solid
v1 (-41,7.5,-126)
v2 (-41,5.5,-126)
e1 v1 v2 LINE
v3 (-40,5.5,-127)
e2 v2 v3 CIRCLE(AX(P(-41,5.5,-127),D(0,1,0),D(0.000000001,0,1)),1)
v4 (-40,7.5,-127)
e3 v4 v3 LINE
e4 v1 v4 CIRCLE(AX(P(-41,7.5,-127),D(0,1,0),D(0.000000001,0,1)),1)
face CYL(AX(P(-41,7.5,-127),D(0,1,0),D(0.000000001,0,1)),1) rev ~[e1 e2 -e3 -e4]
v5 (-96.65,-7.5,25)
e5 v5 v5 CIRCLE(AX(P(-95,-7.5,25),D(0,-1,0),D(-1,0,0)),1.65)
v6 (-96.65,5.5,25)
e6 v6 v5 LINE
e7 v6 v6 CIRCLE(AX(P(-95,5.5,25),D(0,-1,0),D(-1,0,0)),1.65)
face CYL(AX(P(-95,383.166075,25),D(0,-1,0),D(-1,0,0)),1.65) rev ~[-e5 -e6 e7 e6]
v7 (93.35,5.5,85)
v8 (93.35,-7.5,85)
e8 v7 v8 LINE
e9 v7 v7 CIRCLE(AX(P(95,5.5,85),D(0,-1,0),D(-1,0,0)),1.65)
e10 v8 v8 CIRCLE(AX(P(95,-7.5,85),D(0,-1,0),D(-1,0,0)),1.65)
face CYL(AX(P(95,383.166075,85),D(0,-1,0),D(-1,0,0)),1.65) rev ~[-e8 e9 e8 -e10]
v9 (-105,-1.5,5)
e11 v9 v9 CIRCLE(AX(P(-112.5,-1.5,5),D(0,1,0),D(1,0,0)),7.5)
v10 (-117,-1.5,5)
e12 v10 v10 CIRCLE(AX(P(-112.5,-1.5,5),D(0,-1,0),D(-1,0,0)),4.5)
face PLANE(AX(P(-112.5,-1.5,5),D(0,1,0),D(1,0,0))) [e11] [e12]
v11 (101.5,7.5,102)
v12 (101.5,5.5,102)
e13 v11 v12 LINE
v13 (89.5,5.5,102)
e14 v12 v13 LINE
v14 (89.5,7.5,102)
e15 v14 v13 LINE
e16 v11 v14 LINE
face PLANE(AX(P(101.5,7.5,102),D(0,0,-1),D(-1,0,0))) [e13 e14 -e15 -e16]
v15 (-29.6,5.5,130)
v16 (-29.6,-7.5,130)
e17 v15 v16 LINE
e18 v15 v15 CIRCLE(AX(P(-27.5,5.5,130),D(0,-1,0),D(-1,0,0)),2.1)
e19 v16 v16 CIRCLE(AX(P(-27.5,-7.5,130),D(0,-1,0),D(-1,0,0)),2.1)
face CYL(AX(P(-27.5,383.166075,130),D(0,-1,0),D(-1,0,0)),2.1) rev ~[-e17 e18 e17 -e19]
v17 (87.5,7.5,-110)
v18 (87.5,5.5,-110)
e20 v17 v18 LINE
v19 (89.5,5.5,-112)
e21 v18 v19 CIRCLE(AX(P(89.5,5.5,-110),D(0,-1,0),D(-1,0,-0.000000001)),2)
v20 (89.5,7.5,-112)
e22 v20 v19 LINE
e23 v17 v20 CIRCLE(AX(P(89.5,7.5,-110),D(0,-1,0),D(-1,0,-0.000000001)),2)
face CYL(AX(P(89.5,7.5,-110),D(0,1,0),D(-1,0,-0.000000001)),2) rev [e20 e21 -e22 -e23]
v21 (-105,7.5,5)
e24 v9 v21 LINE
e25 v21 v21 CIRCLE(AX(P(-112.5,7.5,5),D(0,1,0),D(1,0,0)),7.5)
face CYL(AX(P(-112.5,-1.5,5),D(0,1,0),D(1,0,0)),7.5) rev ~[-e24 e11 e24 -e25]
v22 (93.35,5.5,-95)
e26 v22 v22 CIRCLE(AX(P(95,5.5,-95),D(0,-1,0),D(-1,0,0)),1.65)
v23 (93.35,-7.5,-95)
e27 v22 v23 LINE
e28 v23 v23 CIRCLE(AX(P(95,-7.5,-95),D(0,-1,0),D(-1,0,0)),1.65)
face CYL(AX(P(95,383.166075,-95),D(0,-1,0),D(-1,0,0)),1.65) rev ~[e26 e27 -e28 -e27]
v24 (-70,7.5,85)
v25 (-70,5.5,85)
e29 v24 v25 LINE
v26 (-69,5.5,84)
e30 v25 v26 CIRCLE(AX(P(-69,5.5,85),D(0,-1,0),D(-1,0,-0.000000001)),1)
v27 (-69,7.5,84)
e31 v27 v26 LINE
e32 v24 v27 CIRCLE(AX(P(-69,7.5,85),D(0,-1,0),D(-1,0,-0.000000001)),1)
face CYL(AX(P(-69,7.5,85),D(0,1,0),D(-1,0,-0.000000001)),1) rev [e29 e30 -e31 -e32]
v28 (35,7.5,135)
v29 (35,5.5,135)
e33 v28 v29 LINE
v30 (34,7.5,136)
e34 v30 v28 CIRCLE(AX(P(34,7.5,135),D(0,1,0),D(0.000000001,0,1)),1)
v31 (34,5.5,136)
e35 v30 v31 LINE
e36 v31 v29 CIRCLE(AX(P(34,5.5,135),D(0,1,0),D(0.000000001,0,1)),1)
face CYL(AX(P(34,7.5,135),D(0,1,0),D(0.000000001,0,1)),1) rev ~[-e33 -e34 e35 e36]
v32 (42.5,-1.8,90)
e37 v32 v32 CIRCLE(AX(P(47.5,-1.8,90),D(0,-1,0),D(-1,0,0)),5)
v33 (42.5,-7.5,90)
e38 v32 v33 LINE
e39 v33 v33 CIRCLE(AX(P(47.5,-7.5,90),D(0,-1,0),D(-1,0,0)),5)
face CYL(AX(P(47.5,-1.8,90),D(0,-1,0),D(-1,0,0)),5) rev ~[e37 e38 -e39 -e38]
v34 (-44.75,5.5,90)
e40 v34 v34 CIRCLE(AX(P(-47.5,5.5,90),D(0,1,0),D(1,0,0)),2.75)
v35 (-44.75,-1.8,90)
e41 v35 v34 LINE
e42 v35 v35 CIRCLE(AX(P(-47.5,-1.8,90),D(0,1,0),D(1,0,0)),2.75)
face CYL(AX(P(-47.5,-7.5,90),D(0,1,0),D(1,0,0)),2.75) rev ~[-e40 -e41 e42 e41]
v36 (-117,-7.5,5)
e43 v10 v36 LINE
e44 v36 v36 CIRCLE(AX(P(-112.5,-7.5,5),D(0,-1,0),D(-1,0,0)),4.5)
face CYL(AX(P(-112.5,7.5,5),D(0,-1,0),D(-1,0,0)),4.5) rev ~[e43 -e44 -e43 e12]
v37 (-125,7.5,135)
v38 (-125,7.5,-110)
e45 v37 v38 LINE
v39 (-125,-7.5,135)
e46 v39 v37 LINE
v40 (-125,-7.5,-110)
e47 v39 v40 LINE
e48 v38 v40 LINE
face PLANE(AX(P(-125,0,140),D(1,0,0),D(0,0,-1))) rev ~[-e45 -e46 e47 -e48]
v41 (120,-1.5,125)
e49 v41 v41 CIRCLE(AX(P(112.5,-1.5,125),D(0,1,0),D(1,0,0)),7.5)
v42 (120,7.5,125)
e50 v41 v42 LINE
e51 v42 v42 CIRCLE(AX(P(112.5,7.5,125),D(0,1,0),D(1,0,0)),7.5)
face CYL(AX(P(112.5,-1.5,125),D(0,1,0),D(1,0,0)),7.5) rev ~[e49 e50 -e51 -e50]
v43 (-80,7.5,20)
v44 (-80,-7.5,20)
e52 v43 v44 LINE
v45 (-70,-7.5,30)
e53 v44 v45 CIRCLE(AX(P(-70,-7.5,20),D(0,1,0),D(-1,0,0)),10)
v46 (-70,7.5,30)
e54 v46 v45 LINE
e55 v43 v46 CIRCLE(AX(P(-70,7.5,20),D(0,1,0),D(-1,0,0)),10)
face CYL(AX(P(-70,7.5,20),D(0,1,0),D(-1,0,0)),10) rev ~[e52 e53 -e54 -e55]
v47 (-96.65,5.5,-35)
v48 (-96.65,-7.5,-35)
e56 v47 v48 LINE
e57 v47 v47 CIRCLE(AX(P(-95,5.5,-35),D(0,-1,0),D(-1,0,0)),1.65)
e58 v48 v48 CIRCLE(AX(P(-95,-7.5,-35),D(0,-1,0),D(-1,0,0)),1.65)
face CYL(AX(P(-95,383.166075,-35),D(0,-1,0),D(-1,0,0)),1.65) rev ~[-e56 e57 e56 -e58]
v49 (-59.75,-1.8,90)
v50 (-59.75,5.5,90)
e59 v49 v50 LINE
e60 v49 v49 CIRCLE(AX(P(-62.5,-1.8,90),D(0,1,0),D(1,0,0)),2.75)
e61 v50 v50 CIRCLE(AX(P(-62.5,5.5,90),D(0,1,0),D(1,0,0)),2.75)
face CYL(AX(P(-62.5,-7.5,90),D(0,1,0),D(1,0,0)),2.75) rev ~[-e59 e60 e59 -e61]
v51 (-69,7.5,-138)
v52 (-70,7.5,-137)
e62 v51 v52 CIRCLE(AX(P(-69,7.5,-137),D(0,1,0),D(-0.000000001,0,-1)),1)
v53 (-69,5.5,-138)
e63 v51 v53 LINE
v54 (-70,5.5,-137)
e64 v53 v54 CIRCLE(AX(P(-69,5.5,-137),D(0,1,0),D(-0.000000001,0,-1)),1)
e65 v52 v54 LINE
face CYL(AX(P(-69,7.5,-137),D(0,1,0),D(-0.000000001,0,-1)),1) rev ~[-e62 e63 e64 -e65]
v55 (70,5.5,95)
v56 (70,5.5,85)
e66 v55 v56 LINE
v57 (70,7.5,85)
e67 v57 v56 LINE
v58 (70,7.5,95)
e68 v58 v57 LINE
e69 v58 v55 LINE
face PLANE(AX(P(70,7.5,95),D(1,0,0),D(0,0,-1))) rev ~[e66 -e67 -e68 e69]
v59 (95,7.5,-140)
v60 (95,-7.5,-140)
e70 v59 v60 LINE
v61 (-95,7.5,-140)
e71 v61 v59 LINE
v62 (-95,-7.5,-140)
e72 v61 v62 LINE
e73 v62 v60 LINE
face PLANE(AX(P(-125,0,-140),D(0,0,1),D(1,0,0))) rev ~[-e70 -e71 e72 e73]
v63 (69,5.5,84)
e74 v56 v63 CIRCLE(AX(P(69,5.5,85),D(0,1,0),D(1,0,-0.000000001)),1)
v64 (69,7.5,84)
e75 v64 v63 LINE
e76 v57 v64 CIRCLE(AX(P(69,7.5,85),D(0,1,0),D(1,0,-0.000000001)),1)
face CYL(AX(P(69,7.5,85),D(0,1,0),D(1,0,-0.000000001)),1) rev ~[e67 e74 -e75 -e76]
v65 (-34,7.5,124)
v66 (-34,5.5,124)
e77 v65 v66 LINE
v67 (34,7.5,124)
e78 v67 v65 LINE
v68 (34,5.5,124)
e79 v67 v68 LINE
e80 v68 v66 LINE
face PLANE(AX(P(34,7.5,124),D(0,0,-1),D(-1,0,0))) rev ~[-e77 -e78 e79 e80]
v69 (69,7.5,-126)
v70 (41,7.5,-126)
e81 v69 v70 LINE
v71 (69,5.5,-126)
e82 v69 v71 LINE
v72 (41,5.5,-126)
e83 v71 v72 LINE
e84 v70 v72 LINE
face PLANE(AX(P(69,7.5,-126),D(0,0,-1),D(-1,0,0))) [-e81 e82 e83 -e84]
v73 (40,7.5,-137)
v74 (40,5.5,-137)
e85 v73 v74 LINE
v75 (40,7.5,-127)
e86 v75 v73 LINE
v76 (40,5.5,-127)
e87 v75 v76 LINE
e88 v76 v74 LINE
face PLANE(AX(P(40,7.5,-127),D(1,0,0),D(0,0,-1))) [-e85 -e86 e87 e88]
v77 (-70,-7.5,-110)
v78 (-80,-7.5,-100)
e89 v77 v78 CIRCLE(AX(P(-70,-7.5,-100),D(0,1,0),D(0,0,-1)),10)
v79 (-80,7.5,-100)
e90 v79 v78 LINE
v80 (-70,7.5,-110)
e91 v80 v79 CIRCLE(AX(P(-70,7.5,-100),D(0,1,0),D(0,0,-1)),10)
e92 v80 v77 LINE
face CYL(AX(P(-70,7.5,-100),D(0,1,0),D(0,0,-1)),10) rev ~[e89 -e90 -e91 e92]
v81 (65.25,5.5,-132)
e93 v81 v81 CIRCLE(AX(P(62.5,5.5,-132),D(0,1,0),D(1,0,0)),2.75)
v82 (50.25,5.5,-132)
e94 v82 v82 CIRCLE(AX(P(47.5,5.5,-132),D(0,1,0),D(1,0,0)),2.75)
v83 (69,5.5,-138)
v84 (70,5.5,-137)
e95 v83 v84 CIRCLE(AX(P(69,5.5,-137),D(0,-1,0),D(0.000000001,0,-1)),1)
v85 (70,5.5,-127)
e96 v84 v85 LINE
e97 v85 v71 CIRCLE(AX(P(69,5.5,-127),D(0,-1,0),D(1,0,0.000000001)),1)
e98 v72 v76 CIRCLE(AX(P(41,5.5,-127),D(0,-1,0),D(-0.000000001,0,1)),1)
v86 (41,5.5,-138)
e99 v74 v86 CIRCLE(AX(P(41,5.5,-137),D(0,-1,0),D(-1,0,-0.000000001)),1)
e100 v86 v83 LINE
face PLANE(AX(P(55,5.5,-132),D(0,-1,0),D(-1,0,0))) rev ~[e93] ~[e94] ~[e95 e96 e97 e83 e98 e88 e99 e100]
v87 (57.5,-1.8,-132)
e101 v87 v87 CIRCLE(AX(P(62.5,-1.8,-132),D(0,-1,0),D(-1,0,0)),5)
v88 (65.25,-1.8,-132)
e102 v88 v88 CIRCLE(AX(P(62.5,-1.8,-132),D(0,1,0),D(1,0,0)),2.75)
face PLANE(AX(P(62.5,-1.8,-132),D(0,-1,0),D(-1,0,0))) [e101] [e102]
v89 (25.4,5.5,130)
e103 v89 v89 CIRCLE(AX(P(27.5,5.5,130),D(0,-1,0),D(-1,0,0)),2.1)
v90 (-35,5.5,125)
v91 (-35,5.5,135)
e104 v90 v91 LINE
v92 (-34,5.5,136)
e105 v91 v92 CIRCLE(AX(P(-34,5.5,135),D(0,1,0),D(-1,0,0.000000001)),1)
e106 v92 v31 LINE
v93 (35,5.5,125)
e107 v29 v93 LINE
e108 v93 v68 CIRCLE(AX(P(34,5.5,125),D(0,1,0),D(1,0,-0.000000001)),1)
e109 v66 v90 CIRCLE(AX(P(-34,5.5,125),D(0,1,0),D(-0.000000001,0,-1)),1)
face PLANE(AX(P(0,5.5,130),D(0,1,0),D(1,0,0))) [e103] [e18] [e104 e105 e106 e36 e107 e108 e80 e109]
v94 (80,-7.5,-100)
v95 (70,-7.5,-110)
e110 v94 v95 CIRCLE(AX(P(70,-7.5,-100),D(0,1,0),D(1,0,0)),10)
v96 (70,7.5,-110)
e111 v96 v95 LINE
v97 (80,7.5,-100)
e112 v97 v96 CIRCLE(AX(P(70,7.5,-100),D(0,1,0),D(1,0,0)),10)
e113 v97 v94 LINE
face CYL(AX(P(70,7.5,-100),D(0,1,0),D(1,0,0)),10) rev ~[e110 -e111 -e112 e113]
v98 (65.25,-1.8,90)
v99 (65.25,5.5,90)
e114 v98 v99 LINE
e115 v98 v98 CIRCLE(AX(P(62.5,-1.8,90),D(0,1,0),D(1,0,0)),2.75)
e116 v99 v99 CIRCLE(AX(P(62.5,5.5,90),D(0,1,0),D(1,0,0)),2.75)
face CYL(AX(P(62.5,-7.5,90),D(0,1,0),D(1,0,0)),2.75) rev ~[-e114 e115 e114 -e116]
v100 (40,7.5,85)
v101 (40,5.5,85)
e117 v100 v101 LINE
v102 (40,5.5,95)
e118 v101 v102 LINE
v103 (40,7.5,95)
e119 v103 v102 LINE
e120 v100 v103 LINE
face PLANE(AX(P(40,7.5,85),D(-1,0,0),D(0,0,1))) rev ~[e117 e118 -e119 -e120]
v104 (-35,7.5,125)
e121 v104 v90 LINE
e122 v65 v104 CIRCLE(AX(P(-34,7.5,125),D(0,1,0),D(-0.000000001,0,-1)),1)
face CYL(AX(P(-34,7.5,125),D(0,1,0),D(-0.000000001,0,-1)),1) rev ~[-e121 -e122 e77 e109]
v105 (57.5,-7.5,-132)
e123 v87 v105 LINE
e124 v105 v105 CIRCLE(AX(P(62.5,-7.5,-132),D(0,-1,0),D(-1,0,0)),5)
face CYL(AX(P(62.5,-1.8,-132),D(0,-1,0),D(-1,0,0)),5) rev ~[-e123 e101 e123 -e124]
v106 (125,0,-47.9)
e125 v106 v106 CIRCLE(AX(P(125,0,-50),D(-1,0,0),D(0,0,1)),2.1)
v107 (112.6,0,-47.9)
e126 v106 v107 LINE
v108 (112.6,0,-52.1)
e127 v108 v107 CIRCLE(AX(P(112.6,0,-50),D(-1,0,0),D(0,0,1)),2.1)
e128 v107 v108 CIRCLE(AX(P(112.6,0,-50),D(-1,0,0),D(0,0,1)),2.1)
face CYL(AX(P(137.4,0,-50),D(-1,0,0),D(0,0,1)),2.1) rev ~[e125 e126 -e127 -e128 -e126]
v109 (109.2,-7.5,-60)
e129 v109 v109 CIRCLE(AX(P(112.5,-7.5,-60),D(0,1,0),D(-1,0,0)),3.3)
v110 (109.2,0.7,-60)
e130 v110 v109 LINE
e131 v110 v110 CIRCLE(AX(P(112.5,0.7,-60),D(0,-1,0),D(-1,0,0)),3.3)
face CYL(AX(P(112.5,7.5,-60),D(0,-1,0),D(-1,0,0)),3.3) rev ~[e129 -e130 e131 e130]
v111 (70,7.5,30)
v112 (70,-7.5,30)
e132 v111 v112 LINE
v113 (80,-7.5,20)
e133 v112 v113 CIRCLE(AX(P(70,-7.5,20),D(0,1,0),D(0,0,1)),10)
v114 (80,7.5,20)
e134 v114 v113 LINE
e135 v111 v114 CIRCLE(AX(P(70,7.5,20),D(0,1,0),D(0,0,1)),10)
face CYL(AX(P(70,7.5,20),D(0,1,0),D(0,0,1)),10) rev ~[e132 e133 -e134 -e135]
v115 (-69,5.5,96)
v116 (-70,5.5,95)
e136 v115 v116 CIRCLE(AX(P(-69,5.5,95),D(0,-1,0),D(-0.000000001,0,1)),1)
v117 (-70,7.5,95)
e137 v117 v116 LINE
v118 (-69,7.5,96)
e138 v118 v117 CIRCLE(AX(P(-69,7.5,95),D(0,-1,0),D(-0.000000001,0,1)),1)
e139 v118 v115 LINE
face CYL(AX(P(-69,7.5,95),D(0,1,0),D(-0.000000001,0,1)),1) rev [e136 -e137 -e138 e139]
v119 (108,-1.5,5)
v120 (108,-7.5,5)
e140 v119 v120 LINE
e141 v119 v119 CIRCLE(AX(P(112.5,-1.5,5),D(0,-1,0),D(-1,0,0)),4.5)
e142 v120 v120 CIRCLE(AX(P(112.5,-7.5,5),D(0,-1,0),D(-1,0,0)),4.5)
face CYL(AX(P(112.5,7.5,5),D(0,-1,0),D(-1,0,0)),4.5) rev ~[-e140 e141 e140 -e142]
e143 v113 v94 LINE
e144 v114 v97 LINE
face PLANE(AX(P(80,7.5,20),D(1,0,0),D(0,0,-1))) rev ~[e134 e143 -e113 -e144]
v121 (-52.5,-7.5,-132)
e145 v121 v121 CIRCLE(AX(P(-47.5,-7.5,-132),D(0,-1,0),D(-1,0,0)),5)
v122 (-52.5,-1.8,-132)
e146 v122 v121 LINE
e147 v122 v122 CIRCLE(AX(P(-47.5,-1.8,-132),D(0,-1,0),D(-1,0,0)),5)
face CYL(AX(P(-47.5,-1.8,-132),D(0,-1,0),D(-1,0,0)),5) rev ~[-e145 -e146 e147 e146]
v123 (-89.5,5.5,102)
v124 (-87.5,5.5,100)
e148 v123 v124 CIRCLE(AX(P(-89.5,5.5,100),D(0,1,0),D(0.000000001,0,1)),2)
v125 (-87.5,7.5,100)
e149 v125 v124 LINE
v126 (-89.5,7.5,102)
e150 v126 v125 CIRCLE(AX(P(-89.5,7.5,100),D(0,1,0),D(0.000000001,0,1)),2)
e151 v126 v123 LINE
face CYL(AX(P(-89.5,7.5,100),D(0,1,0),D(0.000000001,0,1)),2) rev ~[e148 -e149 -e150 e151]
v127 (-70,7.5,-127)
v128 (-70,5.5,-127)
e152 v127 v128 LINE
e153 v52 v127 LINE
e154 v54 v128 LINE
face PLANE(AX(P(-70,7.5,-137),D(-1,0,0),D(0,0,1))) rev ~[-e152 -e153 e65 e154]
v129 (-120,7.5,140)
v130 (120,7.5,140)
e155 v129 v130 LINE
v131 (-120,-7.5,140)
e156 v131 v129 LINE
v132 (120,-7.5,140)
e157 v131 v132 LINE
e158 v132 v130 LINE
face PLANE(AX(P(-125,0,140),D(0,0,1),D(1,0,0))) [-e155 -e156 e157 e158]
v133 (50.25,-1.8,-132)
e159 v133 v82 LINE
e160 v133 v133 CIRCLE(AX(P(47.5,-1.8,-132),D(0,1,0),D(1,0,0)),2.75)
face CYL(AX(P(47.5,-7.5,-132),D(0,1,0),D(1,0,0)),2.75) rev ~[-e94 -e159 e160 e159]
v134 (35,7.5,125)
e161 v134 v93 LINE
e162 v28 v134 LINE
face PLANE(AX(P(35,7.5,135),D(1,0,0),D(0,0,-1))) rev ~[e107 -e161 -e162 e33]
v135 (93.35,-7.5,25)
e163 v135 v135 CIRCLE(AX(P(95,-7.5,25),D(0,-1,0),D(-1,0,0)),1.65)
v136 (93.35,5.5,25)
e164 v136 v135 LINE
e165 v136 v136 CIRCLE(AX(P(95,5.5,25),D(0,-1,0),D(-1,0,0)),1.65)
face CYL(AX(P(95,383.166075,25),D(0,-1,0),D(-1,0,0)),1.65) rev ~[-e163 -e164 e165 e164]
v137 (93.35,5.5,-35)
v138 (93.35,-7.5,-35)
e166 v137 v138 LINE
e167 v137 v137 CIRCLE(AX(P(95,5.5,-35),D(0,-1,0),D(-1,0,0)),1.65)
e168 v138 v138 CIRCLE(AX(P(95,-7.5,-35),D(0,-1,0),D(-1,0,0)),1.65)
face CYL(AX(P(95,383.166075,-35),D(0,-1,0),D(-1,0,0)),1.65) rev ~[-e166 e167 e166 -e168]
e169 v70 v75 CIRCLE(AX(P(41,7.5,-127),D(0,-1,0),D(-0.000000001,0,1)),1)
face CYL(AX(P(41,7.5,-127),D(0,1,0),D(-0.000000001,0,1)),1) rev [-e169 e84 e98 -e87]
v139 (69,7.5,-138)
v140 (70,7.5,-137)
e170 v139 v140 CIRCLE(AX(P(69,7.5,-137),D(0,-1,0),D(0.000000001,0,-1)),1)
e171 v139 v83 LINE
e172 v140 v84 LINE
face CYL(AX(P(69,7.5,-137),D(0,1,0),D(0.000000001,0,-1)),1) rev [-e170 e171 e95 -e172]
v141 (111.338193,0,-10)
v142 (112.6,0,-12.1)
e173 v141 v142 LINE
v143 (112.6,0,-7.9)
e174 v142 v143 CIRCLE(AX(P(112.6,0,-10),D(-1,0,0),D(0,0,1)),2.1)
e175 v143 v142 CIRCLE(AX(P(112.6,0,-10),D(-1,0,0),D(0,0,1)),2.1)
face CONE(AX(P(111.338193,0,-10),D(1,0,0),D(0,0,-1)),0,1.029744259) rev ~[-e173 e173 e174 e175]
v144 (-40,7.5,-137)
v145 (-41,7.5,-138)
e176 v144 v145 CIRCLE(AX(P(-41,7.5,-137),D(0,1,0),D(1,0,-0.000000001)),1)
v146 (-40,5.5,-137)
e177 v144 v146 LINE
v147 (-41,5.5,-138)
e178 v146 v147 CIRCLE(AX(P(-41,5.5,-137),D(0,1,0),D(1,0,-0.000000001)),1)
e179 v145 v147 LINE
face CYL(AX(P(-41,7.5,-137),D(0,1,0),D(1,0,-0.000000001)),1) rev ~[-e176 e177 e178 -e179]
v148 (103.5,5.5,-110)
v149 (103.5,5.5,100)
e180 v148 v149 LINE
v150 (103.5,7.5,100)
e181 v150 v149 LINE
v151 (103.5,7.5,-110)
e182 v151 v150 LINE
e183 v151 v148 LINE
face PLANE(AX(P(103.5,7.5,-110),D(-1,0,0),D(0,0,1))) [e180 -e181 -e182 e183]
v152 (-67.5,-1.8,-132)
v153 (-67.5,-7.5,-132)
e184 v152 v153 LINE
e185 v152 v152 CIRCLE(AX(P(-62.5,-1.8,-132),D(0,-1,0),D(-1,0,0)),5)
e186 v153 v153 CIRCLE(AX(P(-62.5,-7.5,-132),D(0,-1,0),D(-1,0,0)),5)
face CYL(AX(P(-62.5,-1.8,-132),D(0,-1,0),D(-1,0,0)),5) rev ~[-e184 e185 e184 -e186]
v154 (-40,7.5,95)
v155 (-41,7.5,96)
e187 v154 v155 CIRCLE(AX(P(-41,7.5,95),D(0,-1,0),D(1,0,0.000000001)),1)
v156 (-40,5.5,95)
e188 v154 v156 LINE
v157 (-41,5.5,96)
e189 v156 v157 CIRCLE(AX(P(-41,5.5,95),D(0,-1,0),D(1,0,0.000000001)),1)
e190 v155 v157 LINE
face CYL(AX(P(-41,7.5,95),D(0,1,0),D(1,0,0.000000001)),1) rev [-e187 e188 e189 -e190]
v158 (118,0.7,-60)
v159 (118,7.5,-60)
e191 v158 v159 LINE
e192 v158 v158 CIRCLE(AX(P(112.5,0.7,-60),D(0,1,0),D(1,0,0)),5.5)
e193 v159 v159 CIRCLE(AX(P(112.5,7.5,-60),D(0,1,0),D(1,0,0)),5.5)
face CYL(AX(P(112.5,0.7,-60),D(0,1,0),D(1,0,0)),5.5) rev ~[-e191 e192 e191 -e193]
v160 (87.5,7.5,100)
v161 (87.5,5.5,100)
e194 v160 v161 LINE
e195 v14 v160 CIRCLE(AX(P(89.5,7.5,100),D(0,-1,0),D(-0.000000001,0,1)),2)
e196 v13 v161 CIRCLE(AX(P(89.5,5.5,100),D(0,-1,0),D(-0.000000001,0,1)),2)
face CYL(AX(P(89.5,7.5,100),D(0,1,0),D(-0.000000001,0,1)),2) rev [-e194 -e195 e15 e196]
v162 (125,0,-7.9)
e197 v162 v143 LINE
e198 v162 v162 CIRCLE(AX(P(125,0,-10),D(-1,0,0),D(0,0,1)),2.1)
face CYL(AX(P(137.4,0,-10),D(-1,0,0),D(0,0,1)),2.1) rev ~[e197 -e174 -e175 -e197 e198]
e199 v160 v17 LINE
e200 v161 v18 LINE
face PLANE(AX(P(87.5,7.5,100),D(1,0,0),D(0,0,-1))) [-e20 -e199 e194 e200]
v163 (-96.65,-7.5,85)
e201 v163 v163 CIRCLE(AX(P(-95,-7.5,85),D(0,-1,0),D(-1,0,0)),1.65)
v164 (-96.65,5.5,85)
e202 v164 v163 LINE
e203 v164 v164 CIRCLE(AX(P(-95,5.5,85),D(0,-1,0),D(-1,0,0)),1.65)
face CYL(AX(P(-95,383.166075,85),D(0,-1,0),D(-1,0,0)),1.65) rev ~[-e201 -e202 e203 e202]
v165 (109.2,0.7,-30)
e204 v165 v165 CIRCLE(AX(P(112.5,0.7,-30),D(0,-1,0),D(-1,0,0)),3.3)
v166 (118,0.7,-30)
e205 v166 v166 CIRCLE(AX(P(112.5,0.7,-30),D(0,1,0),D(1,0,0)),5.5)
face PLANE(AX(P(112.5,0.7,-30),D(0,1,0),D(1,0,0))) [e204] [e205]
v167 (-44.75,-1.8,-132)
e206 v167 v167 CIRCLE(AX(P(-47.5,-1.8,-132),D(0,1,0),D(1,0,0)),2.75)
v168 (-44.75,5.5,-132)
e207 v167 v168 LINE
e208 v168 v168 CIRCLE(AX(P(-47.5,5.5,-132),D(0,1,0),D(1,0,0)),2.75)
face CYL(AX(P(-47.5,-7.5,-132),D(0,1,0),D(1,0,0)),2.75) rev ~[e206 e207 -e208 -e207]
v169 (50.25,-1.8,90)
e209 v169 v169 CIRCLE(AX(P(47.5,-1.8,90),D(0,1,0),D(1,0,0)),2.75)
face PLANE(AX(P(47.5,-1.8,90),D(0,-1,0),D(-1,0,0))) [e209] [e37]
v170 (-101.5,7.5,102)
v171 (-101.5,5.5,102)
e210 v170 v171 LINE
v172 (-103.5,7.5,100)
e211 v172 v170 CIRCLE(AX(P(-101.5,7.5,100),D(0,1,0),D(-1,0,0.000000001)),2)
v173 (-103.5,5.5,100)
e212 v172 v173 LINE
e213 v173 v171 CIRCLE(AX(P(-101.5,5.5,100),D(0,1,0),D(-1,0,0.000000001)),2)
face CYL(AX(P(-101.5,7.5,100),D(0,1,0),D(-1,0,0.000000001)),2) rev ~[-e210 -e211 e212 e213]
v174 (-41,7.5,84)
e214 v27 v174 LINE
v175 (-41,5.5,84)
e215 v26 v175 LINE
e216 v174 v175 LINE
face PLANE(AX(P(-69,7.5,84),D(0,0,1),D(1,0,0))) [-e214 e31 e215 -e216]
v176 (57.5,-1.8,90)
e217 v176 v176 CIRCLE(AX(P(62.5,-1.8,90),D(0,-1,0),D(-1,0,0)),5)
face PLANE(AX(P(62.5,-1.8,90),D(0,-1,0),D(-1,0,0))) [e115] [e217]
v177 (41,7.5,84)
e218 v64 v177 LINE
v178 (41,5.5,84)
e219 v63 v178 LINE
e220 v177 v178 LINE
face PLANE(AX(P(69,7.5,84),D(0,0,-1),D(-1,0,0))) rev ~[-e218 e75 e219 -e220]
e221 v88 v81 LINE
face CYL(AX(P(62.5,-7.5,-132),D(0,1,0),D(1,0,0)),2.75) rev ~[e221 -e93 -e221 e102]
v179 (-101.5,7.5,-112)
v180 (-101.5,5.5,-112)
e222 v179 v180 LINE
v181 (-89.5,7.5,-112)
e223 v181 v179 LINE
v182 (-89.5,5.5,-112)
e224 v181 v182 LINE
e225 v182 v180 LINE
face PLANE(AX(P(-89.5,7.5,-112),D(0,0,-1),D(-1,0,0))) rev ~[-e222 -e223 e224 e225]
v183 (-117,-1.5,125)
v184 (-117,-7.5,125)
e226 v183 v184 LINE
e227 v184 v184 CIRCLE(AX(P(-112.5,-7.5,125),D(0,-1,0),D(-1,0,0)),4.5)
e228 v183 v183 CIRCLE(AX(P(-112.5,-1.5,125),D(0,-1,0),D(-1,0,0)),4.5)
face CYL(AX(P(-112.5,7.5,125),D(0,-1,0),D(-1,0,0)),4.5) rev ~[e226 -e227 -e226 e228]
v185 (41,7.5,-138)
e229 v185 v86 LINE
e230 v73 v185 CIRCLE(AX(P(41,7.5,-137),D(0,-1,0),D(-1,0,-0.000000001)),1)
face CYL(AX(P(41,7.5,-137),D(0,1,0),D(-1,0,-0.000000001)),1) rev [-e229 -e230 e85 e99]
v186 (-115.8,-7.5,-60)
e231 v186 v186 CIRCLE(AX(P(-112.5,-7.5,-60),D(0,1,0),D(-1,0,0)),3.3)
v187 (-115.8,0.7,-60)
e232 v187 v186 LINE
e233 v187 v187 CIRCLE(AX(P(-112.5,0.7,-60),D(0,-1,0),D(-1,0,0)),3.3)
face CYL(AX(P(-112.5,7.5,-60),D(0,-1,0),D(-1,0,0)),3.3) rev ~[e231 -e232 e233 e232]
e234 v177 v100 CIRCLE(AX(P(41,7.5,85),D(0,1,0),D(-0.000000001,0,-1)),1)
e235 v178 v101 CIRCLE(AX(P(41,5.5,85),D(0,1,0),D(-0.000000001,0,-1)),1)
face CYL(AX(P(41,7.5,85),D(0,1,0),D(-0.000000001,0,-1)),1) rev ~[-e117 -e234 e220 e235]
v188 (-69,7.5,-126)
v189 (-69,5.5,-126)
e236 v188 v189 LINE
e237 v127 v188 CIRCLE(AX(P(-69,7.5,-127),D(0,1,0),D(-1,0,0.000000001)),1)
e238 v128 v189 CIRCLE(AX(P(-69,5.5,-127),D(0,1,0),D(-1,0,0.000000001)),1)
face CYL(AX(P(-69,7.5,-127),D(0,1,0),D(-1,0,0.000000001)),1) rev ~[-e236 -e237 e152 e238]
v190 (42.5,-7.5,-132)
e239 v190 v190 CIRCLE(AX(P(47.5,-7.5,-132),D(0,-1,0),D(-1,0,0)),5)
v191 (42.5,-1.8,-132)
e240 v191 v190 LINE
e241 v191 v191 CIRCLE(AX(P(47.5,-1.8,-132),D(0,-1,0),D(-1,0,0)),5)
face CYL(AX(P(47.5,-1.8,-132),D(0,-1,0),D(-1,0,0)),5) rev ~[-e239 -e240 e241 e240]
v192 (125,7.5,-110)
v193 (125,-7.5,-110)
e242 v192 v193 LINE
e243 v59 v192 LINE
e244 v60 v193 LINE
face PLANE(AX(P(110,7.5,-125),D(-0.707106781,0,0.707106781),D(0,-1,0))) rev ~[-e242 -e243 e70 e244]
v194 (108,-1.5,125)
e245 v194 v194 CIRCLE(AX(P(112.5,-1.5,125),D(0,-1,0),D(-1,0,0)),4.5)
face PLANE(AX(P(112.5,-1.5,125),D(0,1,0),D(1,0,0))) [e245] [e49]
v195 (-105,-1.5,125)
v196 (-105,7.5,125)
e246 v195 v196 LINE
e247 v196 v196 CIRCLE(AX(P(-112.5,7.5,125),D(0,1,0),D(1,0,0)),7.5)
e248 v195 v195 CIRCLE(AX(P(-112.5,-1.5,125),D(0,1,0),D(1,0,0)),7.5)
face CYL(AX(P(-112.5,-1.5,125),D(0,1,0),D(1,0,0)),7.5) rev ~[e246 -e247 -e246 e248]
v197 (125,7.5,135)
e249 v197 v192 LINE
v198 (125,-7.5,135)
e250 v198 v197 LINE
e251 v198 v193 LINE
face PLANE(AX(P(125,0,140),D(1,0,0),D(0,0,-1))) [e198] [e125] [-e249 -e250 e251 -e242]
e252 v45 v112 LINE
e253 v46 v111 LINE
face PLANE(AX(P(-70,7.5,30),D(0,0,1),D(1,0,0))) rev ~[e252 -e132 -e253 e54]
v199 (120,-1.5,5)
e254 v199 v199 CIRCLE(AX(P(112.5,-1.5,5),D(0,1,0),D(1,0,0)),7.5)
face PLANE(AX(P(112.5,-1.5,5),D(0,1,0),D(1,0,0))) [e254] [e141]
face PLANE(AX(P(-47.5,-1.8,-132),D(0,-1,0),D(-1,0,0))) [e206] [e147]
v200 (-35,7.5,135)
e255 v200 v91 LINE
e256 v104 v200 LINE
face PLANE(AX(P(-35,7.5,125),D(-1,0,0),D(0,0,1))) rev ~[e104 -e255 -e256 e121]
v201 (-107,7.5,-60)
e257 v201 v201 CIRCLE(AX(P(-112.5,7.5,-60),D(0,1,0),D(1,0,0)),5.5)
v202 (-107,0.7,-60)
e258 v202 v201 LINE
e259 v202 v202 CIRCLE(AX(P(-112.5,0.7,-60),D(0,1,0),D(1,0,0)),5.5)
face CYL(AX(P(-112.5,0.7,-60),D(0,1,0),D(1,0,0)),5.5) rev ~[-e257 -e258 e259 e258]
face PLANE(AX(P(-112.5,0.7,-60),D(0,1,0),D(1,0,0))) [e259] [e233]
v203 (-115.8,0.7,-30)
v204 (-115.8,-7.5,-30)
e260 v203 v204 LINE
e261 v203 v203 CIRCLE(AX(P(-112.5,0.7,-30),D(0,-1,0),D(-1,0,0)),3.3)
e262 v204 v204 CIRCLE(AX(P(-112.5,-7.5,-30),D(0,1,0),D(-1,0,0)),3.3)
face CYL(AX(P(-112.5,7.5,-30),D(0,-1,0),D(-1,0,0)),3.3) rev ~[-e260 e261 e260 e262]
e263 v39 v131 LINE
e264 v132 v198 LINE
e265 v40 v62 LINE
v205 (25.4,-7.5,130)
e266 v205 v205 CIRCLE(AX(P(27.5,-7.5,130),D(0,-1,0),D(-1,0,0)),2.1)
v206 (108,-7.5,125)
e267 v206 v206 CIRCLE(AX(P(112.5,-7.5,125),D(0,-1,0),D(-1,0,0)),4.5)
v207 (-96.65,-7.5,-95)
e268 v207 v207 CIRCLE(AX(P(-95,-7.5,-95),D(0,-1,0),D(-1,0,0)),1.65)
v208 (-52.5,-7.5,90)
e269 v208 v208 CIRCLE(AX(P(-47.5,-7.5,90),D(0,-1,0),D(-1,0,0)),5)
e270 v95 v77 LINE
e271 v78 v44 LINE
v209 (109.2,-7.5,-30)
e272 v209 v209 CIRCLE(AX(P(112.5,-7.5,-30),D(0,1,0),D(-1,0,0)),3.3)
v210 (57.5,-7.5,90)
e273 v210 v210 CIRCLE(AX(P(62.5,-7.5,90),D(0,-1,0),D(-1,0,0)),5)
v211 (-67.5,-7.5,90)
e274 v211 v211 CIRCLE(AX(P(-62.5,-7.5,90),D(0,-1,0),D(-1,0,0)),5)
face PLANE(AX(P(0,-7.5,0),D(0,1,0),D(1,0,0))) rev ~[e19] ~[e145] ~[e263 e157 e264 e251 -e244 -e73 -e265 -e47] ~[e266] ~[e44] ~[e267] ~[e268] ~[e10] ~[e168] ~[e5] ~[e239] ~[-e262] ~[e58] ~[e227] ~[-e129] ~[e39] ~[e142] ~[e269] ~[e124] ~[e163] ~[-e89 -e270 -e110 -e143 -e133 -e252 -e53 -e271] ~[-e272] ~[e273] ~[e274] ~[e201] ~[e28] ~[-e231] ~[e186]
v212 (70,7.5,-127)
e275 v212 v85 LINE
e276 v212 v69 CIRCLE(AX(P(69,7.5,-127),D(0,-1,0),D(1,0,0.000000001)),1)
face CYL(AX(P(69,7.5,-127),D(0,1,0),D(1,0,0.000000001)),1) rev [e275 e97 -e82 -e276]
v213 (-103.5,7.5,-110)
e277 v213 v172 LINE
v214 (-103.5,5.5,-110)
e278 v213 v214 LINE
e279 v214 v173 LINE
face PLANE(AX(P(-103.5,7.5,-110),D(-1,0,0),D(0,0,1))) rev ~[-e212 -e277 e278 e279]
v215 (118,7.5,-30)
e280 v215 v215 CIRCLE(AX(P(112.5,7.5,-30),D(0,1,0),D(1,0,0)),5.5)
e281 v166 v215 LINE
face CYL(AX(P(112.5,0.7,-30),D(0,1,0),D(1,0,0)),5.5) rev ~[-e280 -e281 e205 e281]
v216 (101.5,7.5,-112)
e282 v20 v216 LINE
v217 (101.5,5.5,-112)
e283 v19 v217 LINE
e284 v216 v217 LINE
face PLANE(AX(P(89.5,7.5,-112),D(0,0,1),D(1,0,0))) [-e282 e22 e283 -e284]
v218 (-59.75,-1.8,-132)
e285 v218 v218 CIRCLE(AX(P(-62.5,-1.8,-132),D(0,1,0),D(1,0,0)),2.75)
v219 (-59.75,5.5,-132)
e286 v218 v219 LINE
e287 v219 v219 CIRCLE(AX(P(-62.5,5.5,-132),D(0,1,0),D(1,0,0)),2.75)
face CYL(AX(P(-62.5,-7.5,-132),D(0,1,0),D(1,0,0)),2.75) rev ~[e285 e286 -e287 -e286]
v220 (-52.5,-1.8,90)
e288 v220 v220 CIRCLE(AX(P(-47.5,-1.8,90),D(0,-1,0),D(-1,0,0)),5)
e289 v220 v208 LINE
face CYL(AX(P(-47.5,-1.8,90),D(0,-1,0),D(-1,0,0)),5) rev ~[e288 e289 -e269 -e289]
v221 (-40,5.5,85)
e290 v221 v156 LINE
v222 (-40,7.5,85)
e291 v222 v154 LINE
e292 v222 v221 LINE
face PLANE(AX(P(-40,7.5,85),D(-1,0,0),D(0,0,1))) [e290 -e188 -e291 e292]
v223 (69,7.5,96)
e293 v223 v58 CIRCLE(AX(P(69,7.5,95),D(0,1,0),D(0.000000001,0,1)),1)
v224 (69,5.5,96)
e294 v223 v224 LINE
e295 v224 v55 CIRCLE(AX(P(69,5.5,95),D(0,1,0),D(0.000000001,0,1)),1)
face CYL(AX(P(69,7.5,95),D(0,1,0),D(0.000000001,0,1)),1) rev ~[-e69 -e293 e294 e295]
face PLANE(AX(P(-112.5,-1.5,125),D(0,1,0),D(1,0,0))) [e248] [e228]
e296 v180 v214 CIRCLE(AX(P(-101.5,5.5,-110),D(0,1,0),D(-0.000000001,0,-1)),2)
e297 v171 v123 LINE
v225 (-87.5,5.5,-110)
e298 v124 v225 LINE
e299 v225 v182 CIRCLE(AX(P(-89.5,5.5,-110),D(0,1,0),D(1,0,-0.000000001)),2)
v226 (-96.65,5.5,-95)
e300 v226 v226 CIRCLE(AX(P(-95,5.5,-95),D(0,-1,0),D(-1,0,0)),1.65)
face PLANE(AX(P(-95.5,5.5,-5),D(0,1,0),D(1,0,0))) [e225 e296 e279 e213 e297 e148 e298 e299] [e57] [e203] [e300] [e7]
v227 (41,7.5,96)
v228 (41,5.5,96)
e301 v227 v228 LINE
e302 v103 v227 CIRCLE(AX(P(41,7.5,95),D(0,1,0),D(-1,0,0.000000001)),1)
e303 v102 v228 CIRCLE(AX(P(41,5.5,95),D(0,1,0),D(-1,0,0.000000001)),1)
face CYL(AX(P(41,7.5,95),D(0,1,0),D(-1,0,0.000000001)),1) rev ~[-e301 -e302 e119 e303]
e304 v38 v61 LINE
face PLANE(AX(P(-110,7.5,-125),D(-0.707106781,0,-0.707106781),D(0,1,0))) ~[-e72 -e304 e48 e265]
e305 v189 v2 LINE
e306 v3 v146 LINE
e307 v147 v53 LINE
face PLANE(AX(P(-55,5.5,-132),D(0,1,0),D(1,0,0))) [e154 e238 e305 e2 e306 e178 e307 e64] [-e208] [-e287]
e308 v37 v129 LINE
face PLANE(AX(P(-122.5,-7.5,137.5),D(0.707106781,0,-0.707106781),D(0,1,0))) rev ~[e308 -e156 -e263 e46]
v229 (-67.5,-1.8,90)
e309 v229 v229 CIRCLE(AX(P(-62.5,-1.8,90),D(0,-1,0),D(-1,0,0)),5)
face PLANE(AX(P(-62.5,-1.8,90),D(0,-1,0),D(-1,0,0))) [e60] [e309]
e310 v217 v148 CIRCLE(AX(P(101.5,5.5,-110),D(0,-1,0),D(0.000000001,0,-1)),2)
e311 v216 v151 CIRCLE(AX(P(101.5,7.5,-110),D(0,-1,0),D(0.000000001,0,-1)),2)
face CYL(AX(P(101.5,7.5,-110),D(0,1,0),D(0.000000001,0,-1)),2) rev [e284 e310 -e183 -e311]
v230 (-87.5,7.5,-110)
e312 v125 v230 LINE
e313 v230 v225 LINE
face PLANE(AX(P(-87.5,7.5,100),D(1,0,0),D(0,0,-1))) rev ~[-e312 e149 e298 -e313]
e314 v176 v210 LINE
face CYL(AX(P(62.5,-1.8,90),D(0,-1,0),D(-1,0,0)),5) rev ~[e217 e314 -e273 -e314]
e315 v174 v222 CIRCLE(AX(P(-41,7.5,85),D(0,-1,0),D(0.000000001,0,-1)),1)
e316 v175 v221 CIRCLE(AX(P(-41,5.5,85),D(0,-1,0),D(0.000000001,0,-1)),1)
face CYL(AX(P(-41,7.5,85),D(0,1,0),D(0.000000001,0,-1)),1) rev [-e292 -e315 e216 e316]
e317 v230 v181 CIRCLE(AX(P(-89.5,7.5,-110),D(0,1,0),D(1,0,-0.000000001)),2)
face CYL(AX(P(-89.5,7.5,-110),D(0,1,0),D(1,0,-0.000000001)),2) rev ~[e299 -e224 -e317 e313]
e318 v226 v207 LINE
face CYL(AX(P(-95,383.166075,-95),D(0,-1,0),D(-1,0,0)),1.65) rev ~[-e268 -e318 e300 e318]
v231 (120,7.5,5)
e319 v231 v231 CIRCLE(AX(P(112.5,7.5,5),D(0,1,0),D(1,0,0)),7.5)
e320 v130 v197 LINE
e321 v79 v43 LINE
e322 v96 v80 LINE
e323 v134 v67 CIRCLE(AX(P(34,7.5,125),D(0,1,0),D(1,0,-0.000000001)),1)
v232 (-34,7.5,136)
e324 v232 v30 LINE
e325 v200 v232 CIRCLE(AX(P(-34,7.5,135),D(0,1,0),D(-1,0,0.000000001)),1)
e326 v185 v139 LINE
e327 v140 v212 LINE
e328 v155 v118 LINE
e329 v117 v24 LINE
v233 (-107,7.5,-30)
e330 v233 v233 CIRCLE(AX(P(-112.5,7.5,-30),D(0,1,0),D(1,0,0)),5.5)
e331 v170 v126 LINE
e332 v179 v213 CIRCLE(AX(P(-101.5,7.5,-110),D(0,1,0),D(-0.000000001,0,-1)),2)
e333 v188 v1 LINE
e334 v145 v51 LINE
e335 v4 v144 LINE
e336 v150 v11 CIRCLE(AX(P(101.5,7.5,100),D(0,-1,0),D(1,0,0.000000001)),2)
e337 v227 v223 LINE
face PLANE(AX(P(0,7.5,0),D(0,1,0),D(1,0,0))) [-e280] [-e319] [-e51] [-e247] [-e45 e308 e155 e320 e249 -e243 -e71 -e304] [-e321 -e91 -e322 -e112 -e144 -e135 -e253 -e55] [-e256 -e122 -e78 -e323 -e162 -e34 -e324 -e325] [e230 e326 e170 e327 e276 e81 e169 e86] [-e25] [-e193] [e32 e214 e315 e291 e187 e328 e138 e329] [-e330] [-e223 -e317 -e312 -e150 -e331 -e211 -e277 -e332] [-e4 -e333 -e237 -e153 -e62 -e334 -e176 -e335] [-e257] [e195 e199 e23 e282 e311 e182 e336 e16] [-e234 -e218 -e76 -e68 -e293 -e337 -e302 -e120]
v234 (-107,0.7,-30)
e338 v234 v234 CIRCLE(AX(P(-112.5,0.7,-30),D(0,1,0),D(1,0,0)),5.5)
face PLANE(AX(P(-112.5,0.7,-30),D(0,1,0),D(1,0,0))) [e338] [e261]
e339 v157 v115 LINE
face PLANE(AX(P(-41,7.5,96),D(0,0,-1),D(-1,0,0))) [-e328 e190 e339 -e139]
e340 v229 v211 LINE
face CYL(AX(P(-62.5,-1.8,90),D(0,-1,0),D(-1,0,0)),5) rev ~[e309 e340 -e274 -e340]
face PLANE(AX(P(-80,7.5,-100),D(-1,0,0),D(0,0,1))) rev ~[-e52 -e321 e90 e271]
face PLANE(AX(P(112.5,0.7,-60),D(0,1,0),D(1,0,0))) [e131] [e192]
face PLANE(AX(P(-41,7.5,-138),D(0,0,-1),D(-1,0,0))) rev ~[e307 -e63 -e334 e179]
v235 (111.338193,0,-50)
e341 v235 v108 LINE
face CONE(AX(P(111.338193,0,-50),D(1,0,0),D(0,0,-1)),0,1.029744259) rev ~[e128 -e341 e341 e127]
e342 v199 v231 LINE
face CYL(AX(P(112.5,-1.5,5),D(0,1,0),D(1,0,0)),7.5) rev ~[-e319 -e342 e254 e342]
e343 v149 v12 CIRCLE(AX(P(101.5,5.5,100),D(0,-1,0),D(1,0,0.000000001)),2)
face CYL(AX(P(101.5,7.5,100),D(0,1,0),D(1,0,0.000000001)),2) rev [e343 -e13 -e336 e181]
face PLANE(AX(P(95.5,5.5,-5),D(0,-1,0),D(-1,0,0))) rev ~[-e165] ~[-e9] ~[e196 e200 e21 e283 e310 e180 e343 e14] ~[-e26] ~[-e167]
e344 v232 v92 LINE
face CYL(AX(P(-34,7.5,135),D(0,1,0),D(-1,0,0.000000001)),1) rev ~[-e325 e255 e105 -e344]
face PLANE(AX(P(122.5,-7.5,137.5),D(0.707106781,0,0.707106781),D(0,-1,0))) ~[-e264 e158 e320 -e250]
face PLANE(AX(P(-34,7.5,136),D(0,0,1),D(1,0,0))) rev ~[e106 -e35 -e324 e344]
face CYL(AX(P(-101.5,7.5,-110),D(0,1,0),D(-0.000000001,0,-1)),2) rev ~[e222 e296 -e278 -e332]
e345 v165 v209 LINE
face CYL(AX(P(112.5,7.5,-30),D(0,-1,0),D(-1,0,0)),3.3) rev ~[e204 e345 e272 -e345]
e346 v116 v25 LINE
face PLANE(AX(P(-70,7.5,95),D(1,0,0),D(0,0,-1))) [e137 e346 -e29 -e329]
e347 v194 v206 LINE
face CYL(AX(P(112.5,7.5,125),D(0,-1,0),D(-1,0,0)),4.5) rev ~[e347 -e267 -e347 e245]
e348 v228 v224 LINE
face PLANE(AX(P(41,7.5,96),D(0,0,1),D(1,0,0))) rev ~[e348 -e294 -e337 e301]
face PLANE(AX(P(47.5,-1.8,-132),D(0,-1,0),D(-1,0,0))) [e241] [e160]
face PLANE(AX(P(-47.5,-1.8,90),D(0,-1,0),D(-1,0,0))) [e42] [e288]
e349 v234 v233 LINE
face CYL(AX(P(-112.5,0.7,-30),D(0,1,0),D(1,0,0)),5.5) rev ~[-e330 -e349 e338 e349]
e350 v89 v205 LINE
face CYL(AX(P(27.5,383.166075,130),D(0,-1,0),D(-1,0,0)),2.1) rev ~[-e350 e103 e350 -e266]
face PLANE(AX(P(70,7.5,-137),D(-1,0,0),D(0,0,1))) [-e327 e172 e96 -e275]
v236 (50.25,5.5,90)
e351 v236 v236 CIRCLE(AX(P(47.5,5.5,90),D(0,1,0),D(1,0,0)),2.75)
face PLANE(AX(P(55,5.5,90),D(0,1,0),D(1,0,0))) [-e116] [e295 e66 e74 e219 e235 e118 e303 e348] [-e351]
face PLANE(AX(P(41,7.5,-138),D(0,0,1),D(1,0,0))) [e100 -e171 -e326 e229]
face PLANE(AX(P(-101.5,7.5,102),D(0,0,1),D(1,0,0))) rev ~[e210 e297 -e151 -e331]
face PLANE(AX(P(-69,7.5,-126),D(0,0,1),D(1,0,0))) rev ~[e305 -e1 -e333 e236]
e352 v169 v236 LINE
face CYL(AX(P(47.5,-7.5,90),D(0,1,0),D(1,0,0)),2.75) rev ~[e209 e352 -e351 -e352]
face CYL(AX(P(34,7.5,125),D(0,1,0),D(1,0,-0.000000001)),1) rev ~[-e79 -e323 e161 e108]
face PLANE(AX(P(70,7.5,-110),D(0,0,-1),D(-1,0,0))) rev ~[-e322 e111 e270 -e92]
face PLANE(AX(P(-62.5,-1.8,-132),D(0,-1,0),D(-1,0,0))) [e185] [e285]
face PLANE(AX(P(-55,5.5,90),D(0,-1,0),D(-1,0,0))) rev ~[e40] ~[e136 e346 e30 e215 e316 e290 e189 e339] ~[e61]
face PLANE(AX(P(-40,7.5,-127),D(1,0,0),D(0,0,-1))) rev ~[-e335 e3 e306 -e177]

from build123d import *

# Parameters (mm, degrees)
SKETCH_1_W                   = 250
SKETCH_1_H                   = 280
EXTRUDE_1_DEPTH              = 7.5
HOLE_WIZARD_M8_2_D           = 9
HOLE_WIZARD_M8_2_CBORE_D     = 15
HOLE_WIZARD_M8_2_CBORE_DEPTH = 9
CUT_EXTRUDE_1_DEPTH          = 15
HOLE_WIZARD_M4_1_D           = 3.3
HOLE_WIZARD_M5_1_D           = 4.2
HOLE_WIZARD_M5_2_D           = 5.5
HOLE_WIZARD_M5_2_CBORE_D     = 10
HOLE_WIZARD_M5_2_CBORE_DEPTH = 5.7
CUT_EXTRUDE_2_DEPTH          = 2
HOLE_WIZARD_M6_1_D           = 6.6
HOLE_WIZARD_M6_1_DEPTH       = 15
HOLE_WIZARD_M6_1_CBORE_D     = 11
HOLE_WIZARD_M6_1_CBORE_DEPTH = 6.8
HOLE_WIZARD_M6_1_TIP         = 1.982840043
CUT_EXTRUDE_3_DEPTH          = 2
CUT_EXTRUDE_4_DEPTH          = 2
CHAMFER_1_SIZE               = 5
CHAMFER_2_SIZE               = 30
HOLE_WIZARD_M5_2_2_D         = 4.2
HOLE_WIZARD_M5_2_2_DEPTH     = 12.4
HOLE_WIZARD_M5_2_2_TIP       = 1.2618073


with BuildPart() as part:
    # 草图1 → 凸台-拉伸1 (new, symmetric)
    with BuildSketch(Plane(origin=(0, 0, 0), x_dir=(1, 0, 0), z_dir=(0, 1, 0))):
        Rectangle(SKETCH_1_W, SKETCH_1_H)
    extrude(amount=EXTRUDE_1_DEPTH, both=True)

    # M8 六角圆柱头螺钉的柱形沉头孔2 (through all)
    with Locations(Plane(origin=(0, 7.5, 0), x_dir=(1, 0, 0), z_dir=(0, 1, 0))):
        with Locations((-112.5, -125), (112.5, -125), (112.5, -5), (-112.5, -5)):
            CounterBoreHole(HOLE_WIZARD_M8_2_D / 2, HOLE_WIZARD_M8_2_CBORE_D / 2, HOLE_WIZARD_M8_2_CBORE_DEPTH)

    # 草图4 → 切除-拉伸1 (cut)
    with BuildSketch(Plane(origin=(0, 7.5, 0), x_dir=(1, 0, 0), z_dir=(0, 1, 0))):
        with BuildLine():
            Line((-70, -30), (70, -30))
            ThreePointArc((70, -30), (77.071067812, -27.071067812), (80, -20))
            Line((80, -20), (80, 100))
            ThreePointArc((80, 100), (77.071067812, 107.071067812), (70, 110))
            Line((70, 110), (-70, 110))
            ThreePointArc((-70, 110), (-77.071067812, 107.071067812), (-80, 100))
            Line((-80, 100), (-80, -20))
            ThreePointArc((-80, -20), (-77.071067812, -27.071067812), (-70, -30))
        make_face()
    extrude(amount=-CUT_EXTRUDE_1_DEPTH, mode=Mode.SUBTRACT)

    # M4 螺纹孔1 (through all)
    with Locations(Plane(origin=(0, 7.5, 0), x_dir=(1, 0, 0), z_dir=(0, 1, 0))):
        with Locations((95, 95), (-95, 95), (-95, 35), (-95, -25), (-95, -85), (95, 35), (95, -25), (95, -85)):
            Hole(HOLE_WIZARD_M4_1_D / 2)

    # M5 螺纹孔1 (through all)
    with Locations(Plane(origin=(0, 7.5, 0), x_dir=(1, 0, 0), z_dir=(0, 1, 0))):
        with Locations((27.5, -130), (-27.5, -130)):
            Hole(HOLE_WIZARD_M5_1_D / 2)

    # Hole Wizard M5 _2 (through all)
    with Locations(Plane(origin=(0, -7.5, 0), x_dir=(-1, 0, 0), z_dir=(0, -1, 0))):
        with Locations((47.5, 132), (62.5, 132), (62.5, -90), (47.5, -90), (-47.5, -90), (-62.5, -90), (-62.5, 132), (-47.5, 132)):
            CounterBoreHole(HOLE_WIZARD_M5_2_D / 2, HOLE_WIZARD_M5_2_CBORE_D / 2, HOLE_WIZARD_M5_2_CBORE_DEPTH)

    # 草图11 → 切除-拉伸2 (cut)
    with BuildSketch(Plane(origin=(0, 7.5, 0), x_dir=(1, 0, 0), z_dir=(0, 1, 0))):
        with BuildLine():
            Line((101.5, -102), (89.5, -102))
            ThreePointArc((89.5, -102), (88.085786438, -101.414213562), (87.5, -100))
            Line((87.5, -100), (87.5, 110))
            ThreePointArc((87.5, 110), (88.085786438, 111.414213562), (89.5, 112))
            Line((89.5, 112), (101.5, 112))
            ThreePointArc((101.5, 112), (102.914213562, 111.414213562), (103.5, 110))
            Line((103.5, 110), (103.5, -100))
            ThreePointArc((103.5, -100), (102.914213562, -101.414213562), (101.5, -102))
        make_face()
        with BuildLine():
            Line((-87.5, -100), (-87.5, 110))
            ThreePointArc((-87.5, 110), (-88.085786438, 111.414213562), (-89.5, 112))
            Line((-89.5, 112), (-101.5, 112))
            ThreePointArc((-101.5, 112), (-102.914213562, 111.414213562), (-103.5, 110))
            Line((-103.5, 110), (-103.5, -100))
            ThreePointArc((-103.5, -100), (-102.914213562, -101.414213562), (-101.5, -102))
            Line((-101.5, -102), (-89.5, -102))
            ThreePointArc((-89.5, -102), (-88.085786438, -101.414213562), (-87.5, -100))
        make_face()
    extrude(amount=-CUT_EXTRUDE_2_DEPTH, mode=Mode.SUBTRACT)

    # M6 六角圆柱头螺钉的柱形沉头孔1
    with Locations(Plane(origin=(0, 7.5, 0), x_dir=(1, 0, 0), z_dir=(0, 1, 0))):
        with Locations((-112.5, 30), (-112.5, 60), (112.5, 60), (112.5, 30)):
            CounterBoreHole(HOLE_WIZARD_M6_1_D / 2, HOLE_WIZARD_M6_1_CBORE_D / 2, HOLE_WIZARD_M6_1_CBORE_DEPTH, depth=HOLE_WIZARD_M6_1_DEPTH)
            with Locations((0, 0, -(HOLE_WIZARD_M6_1_DEPTH + HOLE_WIZARD_M6_1_TIP / 2))):  # 118° drill point
                Cone(0, HOLE_WIZARD_M6_1_D / 2, HOLE_WIZARD_M6_1_TIP, mode=Mode.SUBTRACT)

    # 草图14 → 切除-拉伸3 (cut)
    with BuildSketch(Plane(origin=(0, 7.5, 0), x_dir=(1, 0, 0), z_dir=(0, 1, 0))):
        with BuildLine():
            Line((-41, 138), (-69, 138))
            ThreePointArc((-69, 138), (-69.707106781, 137.707106781), (-70, 137))
            Line((-70, 137), (-70, 127))
            ThreePointArc((-70, 127), (-69.707106781, 126.292893219), (-69, 126))
            Line((-69, 126), (-41, 126))
            ThreePointArc((-41, 126), (-40.292893219, 126.292893219), (-40, 127))
            Line((-40, 127), (-40, 137))
            ThreePointArc((-40, 137), (-40.292893219, 137.707106781), (-41, 138))
        make_face()
        with BuildLine():
            Line((70, 137), (70, 127))
            ThreePointArc((70, 127), (69.707106781, 126.292893219), (69, 126))
            Line((69, 126), (41, 126))
            ThreePointArc((41, 126), (40.292893219, 126.292893219), (40, 127))
            Line((40, 127), (40, 137))
            ThreePointArc((40, 137), (40.292893219, 137.707106781), (41, 138))
            Line((41, 138), (69, 138))
            ThreePointArc((69, 138), (69.707106781, 137.707106781), (70, 137))
        make_face()
        with BuildLine():
            Line((41, -96), (69, -96))
            ThreePointArc((69, -96), (69.707106781, -95.707106781), (70, -95))
            Line((70, -95), (70, -85))
            ThreePointArc((70, -85), (69.707106781, -84.292893219), (69, -84))
            Line((69, -84), (41, -84))
            ThreePointArc((41, -84), (40.292893219, -84.292893219), (40, -85))
            Line((40, -85), (40, -95))
            ThreePointArc((40, -95), (40.292893219, -95.707106781), (41, -96))
        make_face()
        with BuildLine():
            Line((-70, -95), (-70, -85))
            ThreePointArc((-70, -85), (-69.707106781, -84.292893219), (-69, -84))
            Line((-69, -84), (-41, -84))
            ThreePointArc((-41, -84), (-40.292893219, -84.292893219), (-40, -85))
            Line((-40, -85), (-40, -95))
            ThreePointArc((-40, -95), (-40.292893219, -95.707106781), (-41, -96))
            Line((-41, -96), (-69, -96))
            ThreePointArc((-69, -96), (-69.707106781, -95.707106781), (-70, -95))
        make_face()
    extrude(amount=-CUT_EXTRUDE_3_DEPTH, mode=Mode.SUBTRACT)

    # 草图15 → 切除-拉伸4 (cut)
    with BuildSketch(Plane(origin=(0, 7.5, 0), x_dir=(1, 0, 0), z_dir=(0, 1, 0))):
        with BuildLine():
            Line((34, -124), (-34, -124))
            ThreePointArc((-34, -124), (-34.707106781, -124.292893219), (-35, -125))
            Line((-35, -125), (-35, -135))
            ThreePointArc((-35, -135), (-34.707106781, -135.707106781), (-34, -136))
            Line((-34, -136), (34, -136))
            ThreePointArc((34, -136), (34.707106781, -135.707106781), (35, -135))
            Line((35, -135), (35, -125))
            ThreePointArc((35, -125), (34.707106781, -124.292893219), (34, -124))
        make_face()
    extrude(amount=-CUT_EXTRUDE_4_DEPTH, mode=Mode.SUBTRACT)

    # 倒角1
    chamfer_1_edges = [part.edges().sort_by_distance(p)[0] for p in [
        (125, 0, 140),
        (-125, 0, 140),
    ]]
    chamfer(chamfer_1_edges, length=CHAMFER_1_SIZE)

    # 倒角2
    chamfer_2_edges = [part.edges().sort_by_distance(p)[0] for p in [
        (-125, 0, -140),
        (125, 0, -140),
    ]]
    chamfer(chamfer_2_edges, length=CHAMFER_2_SIZE)

    # Hole Wizard M5 _2 2
    with Locations(Plane(origin=(125, 0, 0), x_dir=(0, 0, -1), z_dir=(1, 0, 0))):
        with Locations((10, 0), (50, 0)):
            Hole(HOLE_WIZARD_M5_2_2_D / 2, depth=HOLE_WIZARD_M5_2_2_DEPTH)
            with Locations((0, 0, -(HOLE_WIZARD_M5_2_2_DEPTH + HOLE_WIZARD_M5_2_2_TIP / 2))):  # 118° drill point
                Cone(0, HOLE_WIZARD_M5_2_2_D / 2, HOLE_WIZARD_M5_2_2_TIP, mode=Mode.SUBTRACT)


solid = part.part
